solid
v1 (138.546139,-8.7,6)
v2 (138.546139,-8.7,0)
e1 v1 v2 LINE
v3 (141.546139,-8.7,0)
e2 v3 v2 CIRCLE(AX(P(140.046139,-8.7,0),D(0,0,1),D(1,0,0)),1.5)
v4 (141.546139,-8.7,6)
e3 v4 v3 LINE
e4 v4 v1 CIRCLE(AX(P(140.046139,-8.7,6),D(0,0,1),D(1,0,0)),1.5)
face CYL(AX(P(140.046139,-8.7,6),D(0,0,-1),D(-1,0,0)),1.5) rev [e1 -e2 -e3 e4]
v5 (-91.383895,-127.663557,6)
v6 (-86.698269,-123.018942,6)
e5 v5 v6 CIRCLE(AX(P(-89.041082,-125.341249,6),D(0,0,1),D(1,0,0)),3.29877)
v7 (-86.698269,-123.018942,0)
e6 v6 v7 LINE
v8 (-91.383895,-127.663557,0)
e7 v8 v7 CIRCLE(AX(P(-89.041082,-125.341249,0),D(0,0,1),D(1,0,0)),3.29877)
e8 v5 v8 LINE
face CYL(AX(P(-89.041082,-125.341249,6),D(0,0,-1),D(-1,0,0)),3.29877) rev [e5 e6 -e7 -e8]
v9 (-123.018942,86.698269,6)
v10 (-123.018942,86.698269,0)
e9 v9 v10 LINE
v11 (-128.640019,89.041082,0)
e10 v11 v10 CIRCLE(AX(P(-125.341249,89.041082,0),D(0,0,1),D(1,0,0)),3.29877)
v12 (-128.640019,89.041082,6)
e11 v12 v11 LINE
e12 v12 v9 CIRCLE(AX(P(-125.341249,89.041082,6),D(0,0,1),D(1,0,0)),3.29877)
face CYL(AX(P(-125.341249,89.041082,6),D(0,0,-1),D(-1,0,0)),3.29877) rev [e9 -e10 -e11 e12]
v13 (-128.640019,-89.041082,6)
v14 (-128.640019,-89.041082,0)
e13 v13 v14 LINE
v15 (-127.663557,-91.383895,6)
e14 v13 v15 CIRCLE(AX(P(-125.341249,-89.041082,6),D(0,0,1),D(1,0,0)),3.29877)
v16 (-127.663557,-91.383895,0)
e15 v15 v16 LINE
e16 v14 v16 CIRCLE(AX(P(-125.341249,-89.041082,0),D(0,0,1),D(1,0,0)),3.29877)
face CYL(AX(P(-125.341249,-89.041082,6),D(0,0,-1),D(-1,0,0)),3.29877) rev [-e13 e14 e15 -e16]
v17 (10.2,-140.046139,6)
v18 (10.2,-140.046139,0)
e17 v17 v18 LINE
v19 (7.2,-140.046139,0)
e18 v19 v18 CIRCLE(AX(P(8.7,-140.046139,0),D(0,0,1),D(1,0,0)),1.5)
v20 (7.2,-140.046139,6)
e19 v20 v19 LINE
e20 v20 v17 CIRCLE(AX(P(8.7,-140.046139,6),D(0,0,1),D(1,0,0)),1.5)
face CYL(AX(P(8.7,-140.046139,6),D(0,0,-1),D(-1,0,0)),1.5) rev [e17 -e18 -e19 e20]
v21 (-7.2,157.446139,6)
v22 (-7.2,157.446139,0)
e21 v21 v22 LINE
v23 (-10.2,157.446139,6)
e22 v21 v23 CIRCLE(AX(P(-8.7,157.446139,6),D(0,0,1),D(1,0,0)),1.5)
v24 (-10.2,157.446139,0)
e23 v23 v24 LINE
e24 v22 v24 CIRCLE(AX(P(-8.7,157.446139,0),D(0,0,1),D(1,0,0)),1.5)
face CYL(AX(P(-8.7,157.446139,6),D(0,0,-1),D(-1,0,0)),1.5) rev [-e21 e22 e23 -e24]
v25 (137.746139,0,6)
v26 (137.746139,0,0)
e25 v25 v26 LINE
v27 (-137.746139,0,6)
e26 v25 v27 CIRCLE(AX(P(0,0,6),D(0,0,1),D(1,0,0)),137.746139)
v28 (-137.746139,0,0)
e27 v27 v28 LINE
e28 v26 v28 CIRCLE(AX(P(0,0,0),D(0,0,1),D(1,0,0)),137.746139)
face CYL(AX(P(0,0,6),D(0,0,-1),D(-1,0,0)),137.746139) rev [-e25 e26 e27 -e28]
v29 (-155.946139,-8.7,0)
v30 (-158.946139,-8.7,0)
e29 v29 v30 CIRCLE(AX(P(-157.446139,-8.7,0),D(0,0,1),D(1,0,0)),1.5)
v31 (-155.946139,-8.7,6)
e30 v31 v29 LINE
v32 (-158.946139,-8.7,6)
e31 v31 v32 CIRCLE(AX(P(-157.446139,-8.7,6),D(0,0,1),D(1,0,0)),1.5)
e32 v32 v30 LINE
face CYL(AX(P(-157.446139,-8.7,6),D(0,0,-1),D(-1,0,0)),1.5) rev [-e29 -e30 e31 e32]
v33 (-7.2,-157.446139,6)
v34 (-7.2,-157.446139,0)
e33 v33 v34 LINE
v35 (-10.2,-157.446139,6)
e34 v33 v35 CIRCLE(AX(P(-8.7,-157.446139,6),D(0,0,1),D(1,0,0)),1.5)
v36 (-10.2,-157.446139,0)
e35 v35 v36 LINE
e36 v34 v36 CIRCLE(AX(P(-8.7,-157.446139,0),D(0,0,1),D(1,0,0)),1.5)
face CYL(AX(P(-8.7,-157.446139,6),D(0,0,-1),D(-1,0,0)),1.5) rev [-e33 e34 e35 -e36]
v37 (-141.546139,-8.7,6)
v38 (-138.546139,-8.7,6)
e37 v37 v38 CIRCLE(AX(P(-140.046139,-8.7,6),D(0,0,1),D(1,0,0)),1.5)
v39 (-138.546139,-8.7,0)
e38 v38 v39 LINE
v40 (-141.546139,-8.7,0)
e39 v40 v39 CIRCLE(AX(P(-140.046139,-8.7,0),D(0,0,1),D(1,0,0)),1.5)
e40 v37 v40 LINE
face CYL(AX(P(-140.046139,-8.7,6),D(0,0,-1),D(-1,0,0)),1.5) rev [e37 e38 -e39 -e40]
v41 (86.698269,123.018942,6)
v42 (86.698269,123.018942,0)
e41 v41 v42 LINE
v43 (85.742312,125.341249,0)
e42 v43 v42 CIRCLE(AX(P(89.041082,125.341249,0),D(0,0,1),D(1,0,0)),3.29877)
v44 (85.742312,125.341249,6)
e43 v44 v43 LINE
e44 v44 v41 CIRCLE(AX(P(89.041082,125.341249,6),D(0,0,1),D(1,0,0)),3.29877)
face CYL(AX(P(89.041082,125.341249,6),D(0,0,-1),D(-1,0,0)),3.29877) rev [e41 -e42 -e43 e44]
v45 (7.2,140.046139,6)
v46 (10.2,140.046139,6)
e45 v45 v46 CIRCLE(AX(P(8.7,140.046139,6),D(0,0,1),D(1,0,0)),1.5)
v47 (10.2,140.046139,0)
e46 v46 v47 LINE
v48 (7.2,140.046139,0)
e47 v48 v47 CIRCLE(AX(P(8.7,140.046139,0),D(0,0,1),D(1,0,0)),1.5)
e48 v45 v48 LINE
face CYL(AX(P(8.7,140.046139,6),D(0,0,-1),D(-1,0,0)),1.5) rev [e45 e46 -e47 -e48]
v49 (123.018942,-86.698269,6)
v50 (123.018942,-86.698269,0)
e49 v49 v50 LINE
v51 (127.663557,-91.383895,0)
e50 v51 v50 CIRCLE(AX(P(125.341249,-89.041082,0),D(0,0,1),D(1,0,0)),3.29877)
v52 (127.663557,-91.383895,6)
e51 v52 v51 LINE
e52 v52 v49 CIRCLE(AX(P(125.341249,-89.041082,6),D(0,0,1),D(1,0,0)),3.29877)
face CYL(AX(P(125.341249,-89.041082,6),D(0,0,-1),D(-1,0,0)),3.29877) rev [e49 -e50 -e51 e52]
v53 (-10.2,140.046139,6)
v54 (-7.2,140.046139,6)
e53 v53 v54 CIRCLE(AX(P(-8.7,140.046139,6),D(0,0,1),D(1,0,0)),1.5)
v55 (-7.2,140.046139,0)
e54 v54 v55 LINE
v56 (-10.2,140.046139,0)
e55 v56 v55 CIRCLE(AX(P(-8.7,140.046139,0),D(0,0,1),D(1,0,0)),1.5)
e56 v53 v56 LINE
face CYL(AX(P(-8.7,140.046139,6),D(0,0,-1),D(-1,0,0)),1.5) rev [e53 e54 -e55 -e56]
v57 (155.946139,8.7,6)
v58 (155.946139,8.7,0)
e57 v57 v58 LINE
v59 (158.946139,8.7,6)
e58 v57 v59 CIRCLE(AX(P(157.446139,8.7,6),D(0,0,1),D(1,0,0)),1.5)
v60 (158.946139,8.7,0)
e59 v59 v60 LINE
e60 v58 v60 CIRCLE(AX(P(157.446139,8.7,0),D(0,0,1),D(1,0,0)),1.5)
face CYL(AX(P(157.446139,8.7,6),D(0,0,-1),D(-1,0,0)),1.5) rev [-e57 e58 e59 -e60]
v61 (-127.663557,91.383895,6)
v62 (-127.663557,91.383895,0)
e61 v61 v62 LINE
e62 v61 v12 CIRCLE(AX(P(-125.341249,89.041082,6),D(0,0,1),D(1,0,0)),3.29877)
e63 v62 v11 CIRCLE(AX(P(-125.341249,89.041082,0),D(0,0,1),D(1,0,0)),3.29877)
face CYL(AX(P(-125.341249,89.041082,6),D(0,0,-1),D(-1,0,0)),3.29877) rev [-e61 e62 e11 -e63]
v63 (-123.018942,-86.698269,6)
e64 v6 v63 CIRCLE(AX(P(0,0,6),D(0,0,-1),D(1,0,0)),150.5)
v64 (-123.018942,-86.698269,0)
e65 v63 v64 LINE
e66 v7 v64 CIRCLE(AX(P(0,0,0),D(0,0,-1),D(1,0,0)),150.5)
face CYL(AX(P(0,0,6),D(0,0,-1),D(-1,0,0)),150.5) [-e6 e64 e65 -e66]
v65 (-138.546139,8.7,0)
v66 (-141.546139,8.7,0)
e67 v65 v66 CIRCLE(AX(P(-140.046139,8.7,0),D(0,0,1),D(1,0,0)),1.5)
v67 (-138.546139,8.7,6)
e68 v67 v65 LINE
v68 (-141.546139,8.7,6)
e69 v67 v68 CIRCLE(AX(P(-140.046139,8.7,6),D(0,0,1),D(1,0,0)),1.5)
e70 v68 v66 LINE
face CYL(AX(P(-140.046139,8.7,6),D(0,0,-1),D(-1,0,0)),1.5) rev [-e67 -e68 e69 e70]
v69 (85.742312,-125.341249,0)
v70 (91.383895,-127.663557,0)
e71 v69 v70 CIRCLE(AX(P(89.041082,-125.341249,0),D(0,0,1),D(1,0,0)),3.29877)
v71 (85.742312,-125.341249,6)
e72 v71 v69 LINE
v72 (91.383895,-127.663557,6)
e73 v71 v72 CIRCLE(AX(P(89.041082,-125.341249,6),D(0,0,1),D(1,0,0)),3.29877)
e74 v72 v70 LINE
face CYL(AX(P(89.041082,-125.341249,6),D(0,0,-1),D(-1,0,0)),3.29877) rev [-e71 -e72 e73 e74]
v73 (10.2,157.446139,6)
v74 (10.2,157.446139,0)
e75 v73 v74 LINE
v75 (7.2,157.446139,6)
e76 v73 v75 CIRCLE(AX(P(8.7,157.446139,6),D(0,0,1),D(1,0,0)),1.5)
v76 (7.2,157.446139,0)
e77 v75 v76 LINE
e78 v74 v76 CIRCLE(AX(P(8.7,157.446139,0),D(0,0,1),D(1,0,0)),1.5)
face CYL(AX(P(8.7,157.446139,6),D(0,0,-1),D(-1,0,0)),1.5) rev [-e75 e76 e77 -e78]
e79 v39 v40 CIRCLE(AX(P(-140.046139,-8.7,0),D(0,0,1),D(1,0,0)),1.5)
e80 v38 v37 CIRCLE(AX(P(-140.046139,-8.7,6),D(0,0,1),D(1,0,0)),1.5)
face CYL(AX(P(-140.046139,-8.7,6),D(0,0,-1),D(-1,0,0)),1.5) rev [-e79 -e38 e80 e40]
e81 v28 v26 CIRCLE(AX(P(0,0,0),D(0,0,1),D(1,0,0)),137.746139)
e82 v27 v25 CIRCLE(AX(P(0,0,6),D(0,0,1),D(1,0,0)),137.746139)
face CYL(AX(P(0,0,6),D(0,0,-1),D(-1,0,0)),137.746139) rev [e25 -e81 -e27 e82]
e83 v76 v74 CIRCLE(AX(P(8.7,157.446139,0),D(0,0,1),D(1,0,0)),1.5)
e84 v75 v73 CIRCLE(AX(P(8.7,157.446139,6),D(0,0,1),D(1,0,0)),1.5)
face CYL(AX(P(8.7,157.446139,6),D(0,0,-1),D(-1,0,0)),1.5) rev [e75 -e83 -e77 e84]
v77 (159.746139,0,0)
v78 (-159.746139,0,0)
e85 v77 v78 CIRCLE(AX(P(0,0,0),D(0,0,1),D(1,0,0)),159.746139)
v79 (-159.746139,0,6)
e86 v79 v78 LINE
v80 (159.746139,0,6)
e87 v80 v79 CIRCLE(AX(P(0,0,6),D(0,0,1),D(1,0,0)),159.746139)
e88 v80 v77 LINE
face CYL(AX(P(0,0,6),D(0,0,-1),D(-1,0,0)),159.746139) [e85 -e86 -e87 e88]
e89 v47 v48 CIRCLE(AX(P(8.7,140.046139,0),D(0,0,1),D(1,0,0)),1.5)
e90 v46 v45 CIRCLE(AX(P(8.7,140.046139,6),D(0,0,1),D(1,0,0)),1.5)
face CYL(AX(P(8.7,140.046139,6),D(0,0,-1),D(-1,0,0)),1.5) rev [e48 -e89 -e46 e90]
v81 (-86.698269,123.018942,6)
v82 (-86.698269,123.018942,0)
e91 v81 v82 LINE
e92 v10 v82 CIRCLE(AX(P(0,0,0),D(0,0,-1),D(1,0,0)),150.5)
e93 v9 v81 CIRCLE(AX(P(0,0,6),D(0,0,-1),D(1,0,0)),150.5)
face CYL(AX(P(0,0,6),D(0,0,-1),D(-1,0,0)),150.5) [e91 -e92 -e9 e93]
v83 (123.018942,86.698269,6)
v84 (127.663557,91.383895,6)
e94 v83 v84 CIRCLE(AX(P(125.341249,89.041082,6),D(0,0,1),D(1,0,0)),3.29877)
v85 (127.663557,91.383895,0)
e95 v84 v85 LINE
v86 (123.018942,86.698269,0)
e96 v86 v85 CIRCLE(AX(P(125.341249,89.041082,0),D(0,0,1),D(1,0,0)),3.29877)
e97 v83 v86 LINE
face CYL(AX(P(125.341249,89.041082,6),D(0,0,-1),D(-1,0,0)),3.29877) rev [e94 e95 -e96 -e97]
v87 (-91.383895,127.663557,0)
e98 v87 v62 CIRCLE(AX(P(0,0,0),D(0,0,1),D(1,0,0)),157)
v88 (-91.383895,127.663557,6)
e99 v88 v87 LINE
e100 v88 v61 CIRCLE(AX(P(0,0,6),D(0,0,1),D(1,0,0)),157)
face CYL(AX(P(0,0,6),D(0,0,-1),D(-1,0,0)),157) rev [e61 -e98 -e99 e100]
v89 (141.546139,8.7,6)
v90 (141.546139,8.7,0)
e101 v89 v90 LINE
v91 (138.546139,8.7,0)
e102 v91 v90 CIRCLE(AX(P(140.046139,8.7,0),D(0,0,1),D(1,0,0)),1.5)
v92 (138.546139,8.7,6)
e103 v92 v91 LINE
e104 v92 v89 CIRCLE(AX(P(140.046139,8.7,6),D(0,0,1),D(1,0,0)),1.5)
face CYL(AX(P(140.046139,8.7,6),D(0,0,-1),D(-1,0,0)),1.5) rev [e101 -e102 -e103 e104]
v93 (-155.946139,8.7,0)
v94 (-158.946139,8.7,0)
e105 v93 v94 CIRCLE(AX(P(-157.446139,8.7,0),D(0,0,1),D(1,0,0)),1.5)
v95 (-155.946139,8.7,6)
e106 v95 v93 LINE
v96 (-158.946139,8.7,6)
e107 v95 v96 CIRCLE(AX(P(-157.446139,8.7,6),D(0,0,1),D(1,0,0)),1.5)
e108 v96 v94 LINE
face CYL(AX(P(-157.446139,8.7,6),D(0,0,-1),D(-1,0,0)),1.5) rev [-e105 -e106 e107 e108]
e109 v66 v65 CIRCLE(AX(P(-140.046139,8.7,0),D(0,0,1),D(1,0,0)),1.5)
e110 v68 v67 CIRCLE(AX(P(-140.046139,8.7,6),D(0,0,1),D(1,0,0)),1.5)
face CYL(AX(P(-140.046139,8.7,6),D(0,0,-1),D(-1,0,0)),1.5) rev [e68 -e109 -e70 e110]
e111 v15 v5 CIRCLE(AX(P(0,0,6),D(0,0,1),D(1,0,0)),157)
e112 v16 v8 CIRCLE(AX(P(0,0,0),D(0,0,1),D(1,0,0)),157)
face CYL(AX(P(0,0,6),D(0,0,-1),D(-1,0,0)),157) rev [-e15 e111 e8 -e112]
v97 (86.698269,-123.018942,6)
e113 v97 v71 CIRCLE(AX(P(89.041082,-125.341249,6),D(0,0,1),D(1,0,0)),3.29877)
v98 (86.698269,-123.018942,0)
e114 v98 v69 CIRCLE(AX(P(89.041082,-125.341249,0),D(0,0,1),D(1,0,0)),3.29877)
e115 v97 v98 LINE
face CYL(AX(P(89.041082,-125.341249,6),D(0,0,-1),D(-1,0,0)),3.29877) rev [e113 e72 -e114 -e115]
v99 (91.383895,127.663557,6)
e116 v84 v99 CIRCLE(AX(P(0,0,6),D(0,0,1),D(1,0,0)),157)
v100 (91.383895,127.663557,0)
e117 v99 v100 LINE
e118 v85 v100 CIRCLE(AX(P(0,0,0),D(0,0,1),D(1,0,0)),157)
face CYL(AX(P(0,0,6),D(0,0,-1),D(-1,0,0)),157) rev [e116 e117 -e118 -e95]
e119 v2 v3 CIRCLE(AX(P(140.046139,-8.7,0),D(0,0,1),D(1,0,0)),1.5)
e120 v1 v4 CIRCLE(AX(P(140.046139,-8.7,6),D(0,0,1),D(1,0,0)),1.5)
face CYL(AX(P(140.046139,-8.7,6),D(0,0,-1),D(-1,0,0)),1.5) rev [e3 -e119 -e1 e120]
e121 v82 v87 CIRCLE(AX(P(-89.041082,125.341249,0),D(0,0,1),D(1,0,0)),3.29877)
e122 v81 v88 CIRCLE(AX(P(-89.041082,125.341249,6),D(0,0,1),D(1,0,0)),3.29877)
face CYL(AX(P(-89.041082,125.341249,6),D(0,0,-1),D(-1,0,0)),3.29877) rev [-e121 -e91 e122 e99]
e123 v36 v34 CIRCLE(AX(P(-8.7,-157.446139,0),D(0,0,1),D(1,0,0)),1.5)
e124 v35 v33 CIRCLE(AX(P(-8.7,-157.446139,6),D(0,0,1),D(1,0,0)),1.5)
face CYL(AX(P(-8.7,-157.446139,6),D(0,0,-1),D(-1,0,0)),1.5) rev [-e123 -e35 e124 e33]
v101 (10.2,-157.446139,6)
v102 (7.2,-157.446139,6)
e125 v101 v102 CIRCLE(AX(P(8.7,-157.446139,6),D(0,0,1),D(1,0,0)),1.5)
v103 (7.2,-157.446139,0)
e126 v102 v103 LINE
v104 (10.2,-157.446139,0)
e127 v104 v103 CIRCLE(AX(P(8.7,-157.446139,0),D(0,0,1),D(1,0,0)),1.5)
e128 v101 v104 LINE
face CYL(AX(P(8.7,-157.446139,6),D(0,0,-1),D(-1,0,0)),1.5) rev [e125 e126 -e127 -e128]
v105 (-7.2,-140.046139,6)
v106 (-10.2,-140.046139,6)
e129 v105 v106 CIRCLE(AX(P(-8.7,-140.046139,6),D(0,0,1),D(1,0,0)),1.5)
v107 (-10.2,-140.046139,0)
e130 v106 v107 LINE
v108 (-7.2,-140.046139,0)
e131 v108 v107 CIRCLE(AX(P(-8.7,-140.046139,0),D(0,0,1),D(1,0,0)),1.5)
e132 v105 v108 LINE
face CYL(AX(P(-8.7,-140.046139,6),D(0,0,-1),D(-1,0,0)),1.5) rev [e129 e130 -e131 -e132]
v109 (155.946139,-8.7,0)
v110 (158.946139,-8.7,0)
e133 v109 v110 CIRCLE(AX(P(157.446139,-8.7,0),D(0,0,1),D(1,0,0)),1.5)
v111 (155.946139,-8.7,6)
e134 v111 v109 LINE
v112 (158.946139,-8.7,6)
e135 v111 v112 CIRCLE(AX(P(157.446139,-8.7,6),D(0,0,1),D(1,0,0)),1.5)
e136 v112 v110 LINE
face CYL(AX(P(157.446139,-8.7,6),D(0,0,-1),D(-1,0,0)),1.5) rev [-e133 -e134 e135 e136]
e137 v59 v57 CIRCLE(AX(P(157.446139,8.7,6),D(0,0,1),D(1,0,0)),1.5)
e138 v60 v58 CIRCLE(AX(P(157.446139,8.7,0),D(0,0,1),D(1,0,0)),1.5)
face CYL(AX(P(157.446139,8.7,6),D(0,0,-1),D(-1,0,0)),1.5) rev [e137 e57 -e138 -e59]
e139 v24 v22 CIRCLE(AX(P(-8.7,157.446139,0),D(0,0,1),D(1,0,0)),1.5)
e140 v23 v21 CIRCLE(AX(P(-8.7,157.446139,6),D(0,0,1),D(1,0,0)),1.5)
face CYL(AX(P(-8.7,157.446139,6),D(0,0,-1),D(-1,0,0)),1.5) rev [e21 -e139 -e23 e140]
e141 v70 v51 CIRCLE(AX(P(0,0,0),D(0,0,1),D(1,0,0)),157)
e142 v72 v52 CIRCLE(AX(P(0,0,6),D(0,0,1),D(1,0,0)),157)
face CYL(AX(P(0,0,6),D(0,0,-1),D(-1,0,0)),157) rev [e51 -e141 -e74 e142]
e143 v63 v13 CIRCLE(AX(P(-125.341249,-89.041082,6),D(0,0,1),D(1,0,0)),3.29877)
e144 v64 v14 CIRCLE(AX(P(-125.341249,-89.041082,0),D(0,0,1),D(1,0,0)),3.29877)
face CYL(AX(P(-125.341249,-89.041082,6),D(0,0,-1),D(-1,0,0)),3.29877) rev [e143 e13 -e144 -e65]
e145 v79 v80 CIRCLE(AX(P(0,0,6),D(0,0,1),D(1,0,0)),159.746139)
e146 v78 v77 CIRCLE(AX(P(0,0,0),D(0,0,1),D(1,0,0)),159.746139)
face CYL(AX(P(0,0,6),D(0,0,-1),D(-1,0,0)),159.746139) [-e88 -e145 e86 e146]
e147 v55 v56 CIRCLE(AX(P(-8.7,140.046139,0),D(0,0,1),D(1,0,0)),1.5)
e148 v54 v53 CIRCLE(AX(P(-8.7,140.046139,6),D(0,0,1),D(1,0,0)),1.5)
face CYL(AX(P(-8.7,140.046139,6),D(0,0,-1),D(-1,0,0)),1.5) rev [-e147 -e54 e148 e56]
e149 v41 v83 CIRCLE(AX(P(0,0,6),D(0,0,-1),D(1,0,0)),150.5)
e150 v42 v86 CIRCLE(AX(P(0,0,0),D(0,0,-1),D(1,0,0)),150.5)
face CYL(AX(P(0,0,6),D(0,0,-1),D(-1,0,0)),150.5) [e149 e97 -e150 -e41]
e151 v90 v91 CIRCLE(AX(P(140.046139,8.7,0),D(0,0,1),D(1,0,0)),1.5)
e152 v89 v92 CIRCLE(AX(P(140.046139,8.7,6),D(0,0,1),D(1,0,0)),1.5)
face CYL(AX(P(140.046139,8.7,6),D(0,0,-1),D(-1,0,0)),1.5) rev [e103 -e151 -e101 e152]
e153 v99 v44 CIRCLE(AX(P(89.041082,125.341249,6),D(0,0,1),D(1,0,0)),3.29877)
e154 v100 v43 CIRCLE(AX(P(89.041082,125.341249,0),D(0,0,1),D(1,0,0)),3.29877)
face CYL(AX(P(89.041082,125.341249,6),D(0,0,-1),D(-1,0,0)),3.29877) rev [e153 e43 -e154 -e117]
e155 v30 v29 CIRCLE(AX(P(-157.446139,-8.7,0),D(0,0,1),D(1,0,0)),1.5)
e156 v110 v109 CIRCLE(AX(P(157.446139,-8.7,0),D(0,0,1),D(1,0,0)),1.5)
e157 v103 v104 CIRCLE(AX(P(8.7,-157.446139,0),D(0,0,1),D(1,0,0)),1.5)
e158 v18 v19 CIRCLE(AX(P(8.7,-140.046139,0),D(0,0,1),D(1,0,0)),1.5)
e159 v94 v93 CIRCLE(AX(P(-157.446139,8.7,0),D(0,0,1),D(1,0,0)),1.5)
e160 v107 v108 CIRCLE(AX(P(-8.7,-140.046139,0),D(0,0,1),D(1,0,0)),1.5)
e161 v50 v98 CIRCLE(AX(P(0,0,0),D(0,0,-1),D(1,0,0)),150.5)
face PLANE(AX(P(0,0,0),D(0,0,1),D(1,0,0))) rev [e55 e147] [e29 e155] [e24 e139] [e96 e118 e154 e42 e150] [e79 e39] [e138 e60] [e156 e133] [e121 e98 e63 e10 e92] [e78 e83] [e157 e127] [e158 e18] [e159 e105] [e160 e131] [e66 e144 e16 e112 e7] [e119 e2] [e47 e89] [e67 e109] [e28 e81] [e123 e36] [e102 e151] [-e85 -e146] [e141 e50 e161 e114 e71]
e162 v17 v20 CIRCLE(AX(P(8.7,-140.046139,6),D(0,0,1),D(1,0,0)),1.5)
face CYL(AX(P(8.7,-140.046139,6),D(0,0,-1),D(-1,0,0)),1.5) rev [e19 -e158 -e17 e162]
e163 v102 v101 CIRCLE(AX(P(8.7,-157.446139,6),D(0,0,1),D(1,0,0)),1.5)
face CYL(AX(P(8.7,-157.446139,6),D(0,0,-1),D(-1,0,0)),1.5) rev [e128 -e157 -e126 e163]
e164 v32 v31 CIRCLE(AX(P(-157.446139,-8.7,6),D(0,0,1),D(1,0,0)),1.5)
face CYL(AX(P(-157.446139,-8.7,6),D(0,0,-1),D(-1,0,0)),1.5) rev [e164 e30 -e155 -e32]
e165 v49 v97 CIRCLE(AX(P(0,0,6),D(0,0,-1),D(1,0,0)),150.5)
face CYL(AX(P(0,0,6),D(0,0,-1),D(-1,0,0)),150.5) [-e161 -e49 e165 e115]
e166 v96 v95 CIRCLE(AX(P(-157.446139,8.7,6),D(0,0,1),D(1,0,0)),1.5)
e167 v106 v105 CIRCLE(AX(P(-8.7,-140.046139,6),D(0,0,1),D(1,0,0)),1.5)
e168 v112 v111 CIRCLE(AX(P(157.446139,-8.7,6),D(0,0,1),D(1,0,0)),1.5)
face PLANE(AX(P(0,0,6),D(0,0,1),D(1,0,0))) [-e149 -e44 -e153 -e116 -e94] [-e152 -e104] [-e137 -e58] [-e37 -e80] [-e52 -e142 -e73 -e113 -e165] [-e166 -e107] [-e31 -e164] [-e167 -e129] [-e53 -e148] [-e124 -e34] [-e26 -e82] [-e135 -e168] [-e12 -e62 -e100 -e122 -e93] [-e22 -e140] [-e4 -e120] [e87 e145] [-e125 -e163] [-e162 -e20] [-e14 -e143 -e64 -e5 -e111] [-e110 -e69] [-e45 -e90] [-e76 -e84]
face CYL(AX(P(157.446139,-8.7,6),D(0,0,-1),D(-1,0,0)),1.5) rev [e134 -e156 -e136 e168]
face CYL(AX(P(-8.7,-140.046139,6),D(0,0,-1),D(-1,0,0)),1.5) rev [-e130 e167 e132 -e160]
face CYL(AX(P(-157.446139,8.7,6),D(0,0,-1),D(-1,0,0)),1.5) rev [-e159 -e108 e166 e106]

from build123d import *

# Parameters (mm, degrees)
SKETCH1_R           = 159.746139417
SKETCH1_R_2         = 1.5
SKETCH1_R_3         = 137.746139417
BOSS_EXTRUDE1_DEPTH = 6


with BuildPart() as part:
    # Sketch1 → Boss-Extrude1 (new body)
    with BuildSketch(Plane.XY):
        Circle(SKETCH1_R)
        with BuildLine():
            ThreePointArc((-91.383895087, -127.663556737), (-111.015764646, -111.015764646), (-127.663556737, -91.383895087))
            ThreePointArc((-127.663556737, -91.383895087), (-127.684062187, -86.718774861), (-123.01894196, -86.698269411))
            ThreePointArc((-123.01894196, -86.698269411), (-106.419570569, -106.419570569), (-86.698269411, -123.01894196))
            ThreePointArc((-86.698269411, -123.01894196), (-86.718774861, -127.684062187), (-91.383895087, -127.663556737))
        make_face(mode=Mode.SUBTRACT)
        with Locations((-8.7, -157.446139417)):
            Circle(SKETCH1_R_2, mode=Mode.SUBTRACT)
        with Locations((-8.7, -140.046139417)):
            Circle(SKETCH1_R_2, mode=Mode.SUBTRACT)
        with Locations((-157.446139417, -8.7)):
            Circle(SKETCH1_R_2, mode=Mode.SUBTRACT)
        with Locations((-140.046139417, -8.7)):
            Circle(SKETCH1_R_2, mode=Mode.SUBTRACT)
        with Locations((8.7, -157.446139417)):
            Circle(SKETCH1_R_2, mode=Mode.SUBTRACT)
        with Locations((8.7, -140.046139417)):
            Circle(SKETCH1_R_2, mode=Mode.SUBTRACT)
        with BuildLine():
            ThreePointArc((127.663556737, -91.383895087), (111.015764646, -111.015764646), (91.383895087, -127.663556737))
            ThreePointArc((91.383895087, -127.663556737), (86.718774861, -127.684062187), (86.698269411, -123.01894196))
            ThreePointArc((86.698269411, -123.01894196), (106.419570569, -106.419570569), (123.01894196, -86.698269411))
            ThreePointArc((123.01894196, -86.698269411), (127.684062187, -86.718774861), (127.663556737, -91.383895087))
        make_face(mode=Mode.SUBTRACT)
        with Locations((140.046139417, -8.7)):
            Circle(SKETCH1_R_2, mode=Mode.SUBTRACT)
        with Locations((157.446139417, -8.7)):
            Circle(SKETCH1_R_2, mode=Mode.SUBTRACT)
        with Locations((-157.446139417, 8.7)):
            Circle(SKETCH1_R_2, mode=Mode.SUBTRACT)
        with Locations((-140.046139417, 8.7)):
            Circle(SKETCH1_R_2, mode=Mode.SUBTRACT)
        with BuildLine():
            ThreePointArc((-127.663556737, 91.383895087), (-111.015764646, 111.015764646), (-91.383895087, 127.663556737))
            ThreePointArc((-91.383895087, 127.663556737), (-86.718774861, 127.684062187), (-86.698269411, 123.01894196))
            ThreePointArc((-86.698269411, 123.01894196), (-106.419570569, 106.419570569), (-123.01894196, 86.698269411))
            ThreePointArc((-123.01894196, 86.698269411), (-127.684062187, 86.718774861), (-127.663556737, 91.383895087))
        make_face(mode=Mode.SUBTRACT)
        with Locations((-8.7, 140.046139417)):
            Circle(SKETCH1_R_2, mode=Mode.SUBTRACT)
        with Locations((-8.7, 157.446139417)):
            Circle(SKETCH1_R_2, mode=Mode.SUBTRACT)
        Circle(SKETCH1_R_3, mode=Mode.SUBTRACT)
        with Locations((140.046139417, 8.7)):
            Circle(SKETCH1_R_2, mode=Mode.SUBTRACT)
        with Locations((157.446139417, 8.7)):
            Circle(SKETCH1_R_2, mode=Mode.SUBTRACT)
        with Locations((8.7, 140.046139417)):
            Circle(SKETCH1_R_2, mode=Mode.SUBTRACT)
        with Locations((8.7, 157.446139417)):
            Circle(SKETCH1_R_2, mode=Mode.SUBTRACT)
        with BuildLine():
            ThreePointArc((91.383895087, 127.663556737), (111.015764646, 111.015764646), (127.663556737, 91.383895087))
            ThreePointArc((127.663556737, 91.383895087), (127.684062187, 86.718774861), (123.01894196, 86.698269411))
            ThreePointArc((123.01894196, 86.698269411), (106.419570569, 106.419570569), (86.698269411, 123.01894196))
            ThreePointArc((86.698269411, 123.01894196), (86.718774861, 127.684062187), (91.383895087, 127.663556737))
        make_face(mode=Mode.SUBTRACT)
    extrude(amount=BOSS_EXTRUDE1_DEPTH)


solid = part.part
